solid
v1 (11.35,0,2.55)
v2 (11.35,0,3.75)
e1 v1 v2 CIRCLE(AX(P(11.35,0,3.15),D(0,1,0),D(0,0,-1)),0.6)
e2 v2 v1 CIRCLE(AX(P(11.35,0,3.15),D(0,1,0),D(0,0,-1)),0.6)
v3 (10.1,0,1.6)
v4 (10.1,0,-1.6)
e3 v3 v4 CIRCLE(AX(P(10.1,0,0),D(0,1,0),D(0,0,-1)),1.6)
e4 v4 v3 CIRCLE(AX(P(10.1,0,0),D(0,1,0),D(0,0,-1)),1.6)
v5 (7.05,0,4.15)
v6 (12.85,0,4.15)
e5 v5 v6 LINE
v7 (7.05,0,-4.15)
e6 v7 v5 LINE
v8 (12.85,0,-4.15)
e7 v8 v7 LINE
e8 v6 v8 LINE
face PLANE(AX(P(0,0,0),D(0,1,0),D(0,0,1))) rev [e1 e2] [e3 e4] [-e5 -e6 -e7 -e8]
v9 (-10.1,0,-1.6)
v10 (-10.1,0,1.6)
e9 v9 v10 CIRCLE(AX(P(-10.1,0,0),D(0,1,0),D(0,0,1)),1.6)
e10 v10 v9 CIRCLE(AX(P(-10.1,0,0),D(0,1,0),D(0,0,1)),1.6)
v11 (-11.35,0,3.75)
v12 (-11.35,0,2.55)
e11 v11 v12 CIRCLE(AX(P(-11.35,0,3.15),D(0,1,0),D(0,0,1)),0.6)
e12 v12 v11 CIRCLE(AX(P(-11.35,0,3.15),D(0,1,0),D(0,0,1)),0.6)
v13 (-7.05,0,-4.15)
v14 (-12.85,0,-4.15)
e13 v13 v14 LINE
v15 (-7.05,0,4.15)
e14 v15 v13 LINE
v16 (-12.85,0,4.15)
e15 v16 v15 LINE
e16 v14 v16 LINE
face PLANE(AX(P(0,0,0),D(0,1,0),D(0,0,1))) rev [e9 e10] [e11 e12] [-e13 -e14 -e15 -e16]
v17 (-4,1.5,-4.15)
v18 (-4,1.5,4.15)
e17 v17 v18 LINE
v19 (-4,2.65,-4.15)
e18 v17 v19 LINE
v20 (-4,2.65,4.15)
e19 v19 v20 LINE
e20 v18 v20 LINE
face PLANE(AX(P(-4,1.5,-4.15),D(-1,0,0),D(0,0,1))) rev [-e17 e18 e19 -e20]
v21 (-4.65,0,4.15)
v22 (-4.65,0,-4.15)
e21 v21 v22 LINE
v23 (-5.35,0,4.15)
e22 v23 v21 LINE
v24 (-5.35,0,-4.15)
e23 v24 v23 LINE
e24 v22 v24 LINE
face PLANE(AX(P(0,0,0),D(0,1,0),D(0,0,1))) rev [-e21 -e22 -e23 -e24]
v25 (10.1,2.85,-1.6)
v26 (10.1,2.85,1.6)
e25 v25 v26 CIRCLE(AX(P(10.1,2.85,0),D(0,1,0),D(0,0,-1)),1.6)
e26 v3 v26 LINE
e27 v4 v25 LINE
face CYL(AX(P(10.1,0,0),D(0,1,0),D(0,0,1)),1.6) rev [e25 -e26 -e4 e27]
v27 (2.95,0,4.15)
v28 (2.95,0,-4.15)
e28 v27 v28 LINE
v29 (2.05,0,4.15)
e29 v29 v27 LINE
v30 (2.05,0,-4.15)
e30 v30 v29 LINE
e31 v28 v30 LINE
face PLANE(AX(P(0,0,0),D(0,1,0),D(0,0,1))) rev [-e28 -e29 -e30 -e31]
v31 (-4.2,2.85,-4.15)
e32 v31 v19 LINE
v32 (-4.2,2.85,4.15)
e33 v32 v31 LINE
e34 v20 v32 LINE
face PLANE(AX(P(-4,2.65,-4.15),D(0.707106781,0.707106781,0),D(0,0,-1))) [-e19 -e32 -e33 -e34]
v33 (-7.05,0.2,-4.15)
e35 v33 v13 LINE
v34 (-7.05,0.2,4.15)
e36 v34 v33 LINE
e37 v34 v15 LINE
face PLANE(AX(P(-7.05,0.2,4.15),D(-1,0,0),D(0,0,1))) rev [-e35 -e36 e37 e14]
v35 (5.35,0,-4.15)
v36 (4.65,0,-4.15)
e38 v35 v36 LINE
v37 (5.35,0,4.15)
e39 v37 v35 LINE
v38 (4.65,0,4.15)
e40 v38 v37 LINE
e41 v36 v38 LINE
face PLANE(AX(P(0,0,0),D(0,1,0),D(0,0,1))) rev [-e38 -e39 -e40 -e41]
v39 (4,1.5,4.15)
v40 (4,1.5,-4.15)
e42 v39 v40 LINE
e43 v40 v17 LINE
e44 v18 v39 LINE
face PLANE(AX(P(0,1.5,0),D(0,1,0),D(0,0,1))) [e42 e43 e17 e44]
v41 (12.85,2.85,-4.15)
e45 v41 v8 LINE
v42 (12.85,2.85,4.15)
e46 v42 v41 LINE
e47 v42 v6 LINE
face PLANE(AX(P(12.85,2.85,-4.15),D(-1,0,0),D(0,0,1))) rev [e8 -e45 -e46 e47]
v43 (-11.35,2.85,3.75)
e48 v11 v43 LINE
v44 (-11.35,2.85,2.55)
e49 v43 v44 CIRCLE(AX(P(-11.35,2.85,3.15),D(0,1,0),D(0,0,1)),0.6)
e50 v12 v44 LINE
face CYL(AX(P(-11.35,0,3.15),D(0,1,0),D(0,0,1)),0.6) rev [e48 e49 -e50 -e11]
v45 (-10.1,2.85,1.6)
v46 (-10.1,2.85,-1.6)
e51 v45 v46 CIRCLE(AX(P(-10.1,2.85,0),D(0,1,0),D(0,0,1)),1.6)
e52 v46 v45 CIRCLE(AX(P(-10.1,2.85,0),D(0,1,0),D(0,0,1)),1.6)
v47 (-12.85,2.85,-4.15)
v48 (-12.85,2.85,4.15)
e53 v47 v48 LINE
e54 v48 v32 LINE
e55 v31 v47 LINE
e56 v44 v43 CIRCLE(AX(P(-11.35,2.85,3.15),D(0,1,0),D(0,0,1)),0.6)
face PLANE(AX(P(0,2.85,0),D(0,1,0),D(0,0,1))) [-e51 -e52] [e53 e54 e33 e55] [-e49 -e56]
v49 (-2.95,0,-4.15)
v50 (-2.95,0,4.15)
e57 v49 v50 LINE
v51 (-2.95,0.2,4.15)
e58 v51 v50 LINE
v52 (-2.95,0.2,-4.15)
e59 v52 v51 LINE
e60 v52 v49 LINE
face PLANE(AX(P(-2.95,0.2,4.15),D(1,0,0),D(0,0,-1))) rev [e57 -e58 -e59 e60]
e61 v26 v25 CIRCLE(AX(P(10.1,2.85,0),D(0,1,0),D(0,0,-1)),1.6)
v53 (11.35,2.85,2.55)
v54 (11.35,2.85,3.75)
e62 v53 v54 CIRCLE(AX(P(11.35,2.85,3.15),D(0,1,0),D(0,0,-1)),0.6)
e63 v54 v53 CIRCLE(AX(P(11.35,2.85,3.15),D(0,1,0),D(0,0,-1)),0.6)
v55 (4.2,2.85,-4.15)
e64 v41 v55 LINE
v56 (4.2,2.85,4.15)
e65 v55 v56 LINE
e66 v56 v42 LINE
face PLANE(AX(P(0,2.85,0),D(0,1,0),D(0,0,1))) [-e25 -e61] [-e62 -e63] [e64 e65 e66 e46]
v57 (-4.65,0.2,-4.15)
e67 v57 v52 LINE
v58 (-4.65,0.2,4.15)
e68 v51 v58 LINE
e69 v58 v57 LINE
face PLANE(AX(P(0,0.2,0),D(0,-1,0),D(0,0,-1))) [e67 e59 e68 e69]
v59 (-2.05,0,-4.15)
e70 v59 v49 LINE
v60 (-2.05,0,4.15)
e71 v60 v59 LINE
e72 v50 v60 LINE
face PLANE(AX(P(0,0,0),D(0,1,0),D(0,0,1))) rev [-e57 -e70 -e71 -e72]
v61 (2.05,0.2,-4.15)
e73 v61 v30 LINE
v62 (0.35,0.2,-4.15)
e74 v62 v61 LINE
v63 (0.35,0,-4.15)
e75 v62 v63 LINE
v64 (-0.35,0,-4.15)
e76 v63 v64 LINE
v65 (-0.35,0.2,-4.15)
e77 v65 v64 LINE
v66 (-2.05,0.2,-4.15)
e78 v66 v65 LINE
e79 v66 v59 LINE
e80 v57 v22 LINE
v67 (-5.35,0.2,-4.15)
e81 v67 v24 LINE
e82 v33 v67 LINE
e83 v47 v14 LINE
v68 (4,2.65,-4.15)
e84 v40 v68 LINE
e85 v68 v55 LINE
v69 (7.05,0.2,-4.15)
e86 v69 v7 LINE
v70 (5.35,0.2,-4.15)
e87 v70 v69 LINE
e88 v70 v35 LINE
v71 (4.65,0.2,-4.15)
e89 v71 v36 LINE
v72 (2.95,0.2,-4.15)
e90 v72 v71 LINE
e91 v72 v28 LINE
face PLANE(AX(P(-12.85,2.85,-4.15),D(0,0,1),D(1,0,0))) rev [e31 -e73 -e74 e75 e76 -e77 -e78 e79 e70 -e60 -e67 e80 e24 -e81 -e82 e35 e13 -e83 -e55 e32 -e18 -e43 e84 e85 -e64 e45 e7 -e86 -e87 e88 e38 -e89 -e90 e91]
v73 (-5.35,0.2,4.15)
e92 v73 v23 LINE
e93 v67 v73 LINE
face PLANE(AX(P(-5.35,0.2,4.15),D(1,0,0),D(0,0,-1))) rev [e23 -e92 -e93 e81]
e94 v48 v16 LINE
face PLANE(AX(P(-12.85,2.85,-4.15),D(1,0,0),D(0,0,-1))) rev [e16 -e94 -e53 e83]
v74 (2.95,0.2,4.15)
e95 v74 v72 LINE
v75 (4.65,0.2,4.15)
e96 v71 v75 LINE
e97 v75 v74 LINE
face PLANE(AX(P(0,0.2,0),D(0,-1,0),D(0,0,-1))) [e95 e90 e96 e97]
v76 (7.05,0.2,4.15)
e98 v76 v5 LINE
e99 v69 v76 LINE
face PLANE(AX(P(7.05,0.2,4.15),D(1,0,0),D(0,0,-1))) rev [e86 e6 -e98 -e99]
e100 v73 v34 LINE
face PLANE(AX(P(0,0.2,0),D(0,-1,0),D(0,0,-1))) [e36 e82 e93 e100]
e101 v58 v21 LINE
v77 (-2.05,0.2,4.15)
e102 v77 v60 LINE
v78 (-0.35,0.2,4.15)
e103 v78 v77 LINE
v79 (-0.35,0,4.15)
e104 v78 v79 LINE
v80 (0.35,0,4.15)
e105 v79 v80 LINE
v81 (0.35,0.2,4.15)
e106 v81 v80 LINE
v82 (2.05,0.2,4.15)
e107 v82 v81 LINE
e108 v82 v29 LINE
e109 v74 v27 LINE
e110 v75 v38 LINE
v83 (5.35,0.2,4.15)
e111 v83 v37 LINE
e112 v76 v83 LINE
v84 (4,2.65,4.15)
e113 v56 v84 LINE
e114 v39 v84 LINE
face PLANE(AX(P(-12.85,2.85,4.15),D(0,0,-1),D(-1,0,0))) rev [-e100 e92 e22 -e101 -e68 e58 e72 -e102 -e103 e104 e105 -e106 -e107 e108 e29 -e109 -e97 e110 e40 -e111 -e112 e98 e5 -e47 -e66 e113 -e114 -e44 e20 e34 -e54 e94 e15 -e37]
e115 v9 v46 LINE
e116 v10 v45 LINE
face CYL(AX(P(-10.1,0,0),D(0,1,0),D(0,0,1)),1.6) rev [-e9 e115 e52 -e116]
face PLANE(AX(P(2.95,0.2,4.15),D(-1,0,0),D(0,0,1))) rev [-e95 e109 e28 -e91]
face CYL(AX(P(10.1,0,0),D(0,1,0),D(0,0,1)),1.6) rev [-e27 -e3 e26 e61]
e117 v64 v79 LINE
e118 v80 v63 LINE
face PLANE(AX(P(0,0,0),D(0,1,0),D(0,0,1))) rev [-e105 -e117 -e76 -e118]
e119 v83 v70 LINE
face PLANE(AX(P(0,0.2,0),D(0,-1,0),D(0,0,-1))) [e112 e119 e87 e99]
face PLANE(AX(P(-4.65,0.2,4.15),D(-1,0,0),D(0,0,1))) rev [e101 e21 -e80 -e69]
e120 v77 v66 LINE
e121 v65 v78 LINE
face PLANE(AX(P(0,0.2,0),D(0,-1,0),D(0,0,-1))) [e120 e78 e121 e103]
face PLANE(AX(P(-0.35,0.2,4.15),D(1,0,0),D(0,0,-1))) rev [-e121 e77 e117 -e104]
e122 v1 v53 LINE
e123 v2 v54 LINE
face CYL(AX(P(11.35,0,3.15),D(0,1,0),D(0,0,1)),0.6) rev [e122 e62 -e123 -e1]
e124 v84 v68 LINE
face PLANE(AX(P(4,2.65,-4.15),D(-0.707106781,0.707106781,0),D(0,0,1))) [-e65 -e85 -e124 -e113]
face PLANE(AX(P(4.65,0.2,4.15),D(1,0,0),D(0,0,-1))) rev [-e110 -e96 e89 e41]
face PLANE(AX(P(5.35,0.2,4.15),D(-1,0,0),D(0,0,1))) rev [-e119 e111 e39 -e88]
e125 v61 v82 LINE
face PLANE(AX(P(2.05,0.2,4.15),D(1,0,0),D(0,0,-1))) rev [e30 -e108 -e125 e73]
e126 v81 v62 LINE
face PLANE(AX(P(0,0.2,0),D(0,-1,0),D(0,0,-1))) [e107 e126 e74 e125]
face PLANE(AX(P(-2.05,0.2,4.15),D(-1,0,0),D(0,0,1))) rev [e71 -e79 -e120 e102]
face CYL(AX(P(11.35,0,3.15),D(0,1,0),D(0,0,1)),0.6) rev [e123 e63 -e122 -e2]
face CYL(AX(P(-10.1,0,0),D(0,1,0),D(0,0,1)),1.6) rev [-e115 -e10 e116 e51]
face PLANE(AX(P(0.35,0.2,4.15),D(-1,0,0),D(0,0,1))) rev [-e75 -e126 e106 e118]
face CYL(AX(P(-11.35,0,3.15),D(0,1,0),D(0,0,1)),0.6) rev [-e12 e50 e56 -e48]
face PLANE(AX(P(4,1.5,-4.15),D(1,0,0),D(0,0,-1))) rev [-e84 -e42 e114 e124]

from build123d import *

# Parameters (mm, degrees)
SKETCH1_W           = 25.7
SKETCH1_H           = 8.3
BOSS_EXTRUDE1_DEPTH = 2.85
SKETCH2_R           = 1.6
SKETCH2_R_2         = 0.6
CUT_EXTRUDE1_DEPTH  = 14.800996341
SKETCH3_W           = 1.7
SKETCH3_H           = 8.3
CUT_EXTRUDE2_DEPTH  = 0.2
SKETCH4_W           = 8
SKETCH4_H           = 8.3
CUT_EXTRUDE3_DEPTH  = 1.35
CHAMFER1_SIZE       = 0.2


with BuildPart() as part:
    # Sketch1 → Boss-Extrude1 (new body)
    with BuildSketch(Plane(origin=(0, 0, 0), x_dir=(1, 0, 0), z_dir=(0, 1, 0))):
        Rectangle(SKETCH1_W, SKETCH1_H)
    extrude(amount=BOSS_EXTRUDE1_DEPTH)

    # Sketch2 → Cut-Extrude1 (cut, through all)
    with BuildSketch(Plane(origin=(0, 2.85, 0), x_dir=(1, 0, 0), z_dir=(0, 1, 0))):
        with Locations(Location((-10.1, 0, 0), (0, 0, 270))):
            Circle(SKETCH2_R)
        with Locations(Location((-11.35, -3.15, 0), (0, 0, 270))):
            Circle(SKETCH2_R_2)
        with Locations(Location((10.1, 0, 0), (0, 0, 90))):
            Circle(SKETCH2_R)
        with Locations(Location((11.35, -3.15, 0), (0, 0, 90))):
            Circle(SKETCH2_R_2)
    extrude(amount=-CUT_EXTRUDE1_DEPTH, mode=Mode.SUBTRACT)

    # Sketch3 → Cut-Extrude2 (cut)
    with BuildSketch(Plane.XZ):
        with Locations((-6.2, 0)):
            Rectangle(SKETCH3_W, SKETCH3_H)
        with Locations((1.2, 0)):
            Rectangle(SKETCH3_W, SKETCH3_H)
        with Locations((-3.8, 0)):
            Rectangle(SKETCH3_W, SKETCH3_H)
        with Locations((-1.2, 0)):
            Rectangle(SKETCH3_W, SKETCH3_H)
        with Locations((3.8, 0)):
            Rectangle(SKETCH3_W, SKETCH3_H)
        with Locations((6.2, 0)):
            Rectangle(SKETCH3_W, SKETCH3_H)
    extrude(amount=-CUT_EXTRUDE2_DEPTH, mode=Mode.SUBTRACT)

    # Sketch4 → Cut-Extrude3 (cut)
    with BuildSketch(Plane(origin=(0, 2.85, 0), x_dir=(1, 0, 0), z_dir=(0, 1, 0))):
        Rectangle(SKETCH4_W, SKETCH4_H)
    extrude(amount=-CUT_EXTRUDE3_DEPTH, mode=Mode.SUBTRACT)

    # Chamfer1
    chamfer1_edges = [part.edges().sort_by_distance(p)[0] for p in [
        (4, 2.85, 0),
        (-4, 2.85, 0),
    ]]
    chamfer(chamfer1_edges, length=CHAMFER1_SIZE)


solid = part.part
